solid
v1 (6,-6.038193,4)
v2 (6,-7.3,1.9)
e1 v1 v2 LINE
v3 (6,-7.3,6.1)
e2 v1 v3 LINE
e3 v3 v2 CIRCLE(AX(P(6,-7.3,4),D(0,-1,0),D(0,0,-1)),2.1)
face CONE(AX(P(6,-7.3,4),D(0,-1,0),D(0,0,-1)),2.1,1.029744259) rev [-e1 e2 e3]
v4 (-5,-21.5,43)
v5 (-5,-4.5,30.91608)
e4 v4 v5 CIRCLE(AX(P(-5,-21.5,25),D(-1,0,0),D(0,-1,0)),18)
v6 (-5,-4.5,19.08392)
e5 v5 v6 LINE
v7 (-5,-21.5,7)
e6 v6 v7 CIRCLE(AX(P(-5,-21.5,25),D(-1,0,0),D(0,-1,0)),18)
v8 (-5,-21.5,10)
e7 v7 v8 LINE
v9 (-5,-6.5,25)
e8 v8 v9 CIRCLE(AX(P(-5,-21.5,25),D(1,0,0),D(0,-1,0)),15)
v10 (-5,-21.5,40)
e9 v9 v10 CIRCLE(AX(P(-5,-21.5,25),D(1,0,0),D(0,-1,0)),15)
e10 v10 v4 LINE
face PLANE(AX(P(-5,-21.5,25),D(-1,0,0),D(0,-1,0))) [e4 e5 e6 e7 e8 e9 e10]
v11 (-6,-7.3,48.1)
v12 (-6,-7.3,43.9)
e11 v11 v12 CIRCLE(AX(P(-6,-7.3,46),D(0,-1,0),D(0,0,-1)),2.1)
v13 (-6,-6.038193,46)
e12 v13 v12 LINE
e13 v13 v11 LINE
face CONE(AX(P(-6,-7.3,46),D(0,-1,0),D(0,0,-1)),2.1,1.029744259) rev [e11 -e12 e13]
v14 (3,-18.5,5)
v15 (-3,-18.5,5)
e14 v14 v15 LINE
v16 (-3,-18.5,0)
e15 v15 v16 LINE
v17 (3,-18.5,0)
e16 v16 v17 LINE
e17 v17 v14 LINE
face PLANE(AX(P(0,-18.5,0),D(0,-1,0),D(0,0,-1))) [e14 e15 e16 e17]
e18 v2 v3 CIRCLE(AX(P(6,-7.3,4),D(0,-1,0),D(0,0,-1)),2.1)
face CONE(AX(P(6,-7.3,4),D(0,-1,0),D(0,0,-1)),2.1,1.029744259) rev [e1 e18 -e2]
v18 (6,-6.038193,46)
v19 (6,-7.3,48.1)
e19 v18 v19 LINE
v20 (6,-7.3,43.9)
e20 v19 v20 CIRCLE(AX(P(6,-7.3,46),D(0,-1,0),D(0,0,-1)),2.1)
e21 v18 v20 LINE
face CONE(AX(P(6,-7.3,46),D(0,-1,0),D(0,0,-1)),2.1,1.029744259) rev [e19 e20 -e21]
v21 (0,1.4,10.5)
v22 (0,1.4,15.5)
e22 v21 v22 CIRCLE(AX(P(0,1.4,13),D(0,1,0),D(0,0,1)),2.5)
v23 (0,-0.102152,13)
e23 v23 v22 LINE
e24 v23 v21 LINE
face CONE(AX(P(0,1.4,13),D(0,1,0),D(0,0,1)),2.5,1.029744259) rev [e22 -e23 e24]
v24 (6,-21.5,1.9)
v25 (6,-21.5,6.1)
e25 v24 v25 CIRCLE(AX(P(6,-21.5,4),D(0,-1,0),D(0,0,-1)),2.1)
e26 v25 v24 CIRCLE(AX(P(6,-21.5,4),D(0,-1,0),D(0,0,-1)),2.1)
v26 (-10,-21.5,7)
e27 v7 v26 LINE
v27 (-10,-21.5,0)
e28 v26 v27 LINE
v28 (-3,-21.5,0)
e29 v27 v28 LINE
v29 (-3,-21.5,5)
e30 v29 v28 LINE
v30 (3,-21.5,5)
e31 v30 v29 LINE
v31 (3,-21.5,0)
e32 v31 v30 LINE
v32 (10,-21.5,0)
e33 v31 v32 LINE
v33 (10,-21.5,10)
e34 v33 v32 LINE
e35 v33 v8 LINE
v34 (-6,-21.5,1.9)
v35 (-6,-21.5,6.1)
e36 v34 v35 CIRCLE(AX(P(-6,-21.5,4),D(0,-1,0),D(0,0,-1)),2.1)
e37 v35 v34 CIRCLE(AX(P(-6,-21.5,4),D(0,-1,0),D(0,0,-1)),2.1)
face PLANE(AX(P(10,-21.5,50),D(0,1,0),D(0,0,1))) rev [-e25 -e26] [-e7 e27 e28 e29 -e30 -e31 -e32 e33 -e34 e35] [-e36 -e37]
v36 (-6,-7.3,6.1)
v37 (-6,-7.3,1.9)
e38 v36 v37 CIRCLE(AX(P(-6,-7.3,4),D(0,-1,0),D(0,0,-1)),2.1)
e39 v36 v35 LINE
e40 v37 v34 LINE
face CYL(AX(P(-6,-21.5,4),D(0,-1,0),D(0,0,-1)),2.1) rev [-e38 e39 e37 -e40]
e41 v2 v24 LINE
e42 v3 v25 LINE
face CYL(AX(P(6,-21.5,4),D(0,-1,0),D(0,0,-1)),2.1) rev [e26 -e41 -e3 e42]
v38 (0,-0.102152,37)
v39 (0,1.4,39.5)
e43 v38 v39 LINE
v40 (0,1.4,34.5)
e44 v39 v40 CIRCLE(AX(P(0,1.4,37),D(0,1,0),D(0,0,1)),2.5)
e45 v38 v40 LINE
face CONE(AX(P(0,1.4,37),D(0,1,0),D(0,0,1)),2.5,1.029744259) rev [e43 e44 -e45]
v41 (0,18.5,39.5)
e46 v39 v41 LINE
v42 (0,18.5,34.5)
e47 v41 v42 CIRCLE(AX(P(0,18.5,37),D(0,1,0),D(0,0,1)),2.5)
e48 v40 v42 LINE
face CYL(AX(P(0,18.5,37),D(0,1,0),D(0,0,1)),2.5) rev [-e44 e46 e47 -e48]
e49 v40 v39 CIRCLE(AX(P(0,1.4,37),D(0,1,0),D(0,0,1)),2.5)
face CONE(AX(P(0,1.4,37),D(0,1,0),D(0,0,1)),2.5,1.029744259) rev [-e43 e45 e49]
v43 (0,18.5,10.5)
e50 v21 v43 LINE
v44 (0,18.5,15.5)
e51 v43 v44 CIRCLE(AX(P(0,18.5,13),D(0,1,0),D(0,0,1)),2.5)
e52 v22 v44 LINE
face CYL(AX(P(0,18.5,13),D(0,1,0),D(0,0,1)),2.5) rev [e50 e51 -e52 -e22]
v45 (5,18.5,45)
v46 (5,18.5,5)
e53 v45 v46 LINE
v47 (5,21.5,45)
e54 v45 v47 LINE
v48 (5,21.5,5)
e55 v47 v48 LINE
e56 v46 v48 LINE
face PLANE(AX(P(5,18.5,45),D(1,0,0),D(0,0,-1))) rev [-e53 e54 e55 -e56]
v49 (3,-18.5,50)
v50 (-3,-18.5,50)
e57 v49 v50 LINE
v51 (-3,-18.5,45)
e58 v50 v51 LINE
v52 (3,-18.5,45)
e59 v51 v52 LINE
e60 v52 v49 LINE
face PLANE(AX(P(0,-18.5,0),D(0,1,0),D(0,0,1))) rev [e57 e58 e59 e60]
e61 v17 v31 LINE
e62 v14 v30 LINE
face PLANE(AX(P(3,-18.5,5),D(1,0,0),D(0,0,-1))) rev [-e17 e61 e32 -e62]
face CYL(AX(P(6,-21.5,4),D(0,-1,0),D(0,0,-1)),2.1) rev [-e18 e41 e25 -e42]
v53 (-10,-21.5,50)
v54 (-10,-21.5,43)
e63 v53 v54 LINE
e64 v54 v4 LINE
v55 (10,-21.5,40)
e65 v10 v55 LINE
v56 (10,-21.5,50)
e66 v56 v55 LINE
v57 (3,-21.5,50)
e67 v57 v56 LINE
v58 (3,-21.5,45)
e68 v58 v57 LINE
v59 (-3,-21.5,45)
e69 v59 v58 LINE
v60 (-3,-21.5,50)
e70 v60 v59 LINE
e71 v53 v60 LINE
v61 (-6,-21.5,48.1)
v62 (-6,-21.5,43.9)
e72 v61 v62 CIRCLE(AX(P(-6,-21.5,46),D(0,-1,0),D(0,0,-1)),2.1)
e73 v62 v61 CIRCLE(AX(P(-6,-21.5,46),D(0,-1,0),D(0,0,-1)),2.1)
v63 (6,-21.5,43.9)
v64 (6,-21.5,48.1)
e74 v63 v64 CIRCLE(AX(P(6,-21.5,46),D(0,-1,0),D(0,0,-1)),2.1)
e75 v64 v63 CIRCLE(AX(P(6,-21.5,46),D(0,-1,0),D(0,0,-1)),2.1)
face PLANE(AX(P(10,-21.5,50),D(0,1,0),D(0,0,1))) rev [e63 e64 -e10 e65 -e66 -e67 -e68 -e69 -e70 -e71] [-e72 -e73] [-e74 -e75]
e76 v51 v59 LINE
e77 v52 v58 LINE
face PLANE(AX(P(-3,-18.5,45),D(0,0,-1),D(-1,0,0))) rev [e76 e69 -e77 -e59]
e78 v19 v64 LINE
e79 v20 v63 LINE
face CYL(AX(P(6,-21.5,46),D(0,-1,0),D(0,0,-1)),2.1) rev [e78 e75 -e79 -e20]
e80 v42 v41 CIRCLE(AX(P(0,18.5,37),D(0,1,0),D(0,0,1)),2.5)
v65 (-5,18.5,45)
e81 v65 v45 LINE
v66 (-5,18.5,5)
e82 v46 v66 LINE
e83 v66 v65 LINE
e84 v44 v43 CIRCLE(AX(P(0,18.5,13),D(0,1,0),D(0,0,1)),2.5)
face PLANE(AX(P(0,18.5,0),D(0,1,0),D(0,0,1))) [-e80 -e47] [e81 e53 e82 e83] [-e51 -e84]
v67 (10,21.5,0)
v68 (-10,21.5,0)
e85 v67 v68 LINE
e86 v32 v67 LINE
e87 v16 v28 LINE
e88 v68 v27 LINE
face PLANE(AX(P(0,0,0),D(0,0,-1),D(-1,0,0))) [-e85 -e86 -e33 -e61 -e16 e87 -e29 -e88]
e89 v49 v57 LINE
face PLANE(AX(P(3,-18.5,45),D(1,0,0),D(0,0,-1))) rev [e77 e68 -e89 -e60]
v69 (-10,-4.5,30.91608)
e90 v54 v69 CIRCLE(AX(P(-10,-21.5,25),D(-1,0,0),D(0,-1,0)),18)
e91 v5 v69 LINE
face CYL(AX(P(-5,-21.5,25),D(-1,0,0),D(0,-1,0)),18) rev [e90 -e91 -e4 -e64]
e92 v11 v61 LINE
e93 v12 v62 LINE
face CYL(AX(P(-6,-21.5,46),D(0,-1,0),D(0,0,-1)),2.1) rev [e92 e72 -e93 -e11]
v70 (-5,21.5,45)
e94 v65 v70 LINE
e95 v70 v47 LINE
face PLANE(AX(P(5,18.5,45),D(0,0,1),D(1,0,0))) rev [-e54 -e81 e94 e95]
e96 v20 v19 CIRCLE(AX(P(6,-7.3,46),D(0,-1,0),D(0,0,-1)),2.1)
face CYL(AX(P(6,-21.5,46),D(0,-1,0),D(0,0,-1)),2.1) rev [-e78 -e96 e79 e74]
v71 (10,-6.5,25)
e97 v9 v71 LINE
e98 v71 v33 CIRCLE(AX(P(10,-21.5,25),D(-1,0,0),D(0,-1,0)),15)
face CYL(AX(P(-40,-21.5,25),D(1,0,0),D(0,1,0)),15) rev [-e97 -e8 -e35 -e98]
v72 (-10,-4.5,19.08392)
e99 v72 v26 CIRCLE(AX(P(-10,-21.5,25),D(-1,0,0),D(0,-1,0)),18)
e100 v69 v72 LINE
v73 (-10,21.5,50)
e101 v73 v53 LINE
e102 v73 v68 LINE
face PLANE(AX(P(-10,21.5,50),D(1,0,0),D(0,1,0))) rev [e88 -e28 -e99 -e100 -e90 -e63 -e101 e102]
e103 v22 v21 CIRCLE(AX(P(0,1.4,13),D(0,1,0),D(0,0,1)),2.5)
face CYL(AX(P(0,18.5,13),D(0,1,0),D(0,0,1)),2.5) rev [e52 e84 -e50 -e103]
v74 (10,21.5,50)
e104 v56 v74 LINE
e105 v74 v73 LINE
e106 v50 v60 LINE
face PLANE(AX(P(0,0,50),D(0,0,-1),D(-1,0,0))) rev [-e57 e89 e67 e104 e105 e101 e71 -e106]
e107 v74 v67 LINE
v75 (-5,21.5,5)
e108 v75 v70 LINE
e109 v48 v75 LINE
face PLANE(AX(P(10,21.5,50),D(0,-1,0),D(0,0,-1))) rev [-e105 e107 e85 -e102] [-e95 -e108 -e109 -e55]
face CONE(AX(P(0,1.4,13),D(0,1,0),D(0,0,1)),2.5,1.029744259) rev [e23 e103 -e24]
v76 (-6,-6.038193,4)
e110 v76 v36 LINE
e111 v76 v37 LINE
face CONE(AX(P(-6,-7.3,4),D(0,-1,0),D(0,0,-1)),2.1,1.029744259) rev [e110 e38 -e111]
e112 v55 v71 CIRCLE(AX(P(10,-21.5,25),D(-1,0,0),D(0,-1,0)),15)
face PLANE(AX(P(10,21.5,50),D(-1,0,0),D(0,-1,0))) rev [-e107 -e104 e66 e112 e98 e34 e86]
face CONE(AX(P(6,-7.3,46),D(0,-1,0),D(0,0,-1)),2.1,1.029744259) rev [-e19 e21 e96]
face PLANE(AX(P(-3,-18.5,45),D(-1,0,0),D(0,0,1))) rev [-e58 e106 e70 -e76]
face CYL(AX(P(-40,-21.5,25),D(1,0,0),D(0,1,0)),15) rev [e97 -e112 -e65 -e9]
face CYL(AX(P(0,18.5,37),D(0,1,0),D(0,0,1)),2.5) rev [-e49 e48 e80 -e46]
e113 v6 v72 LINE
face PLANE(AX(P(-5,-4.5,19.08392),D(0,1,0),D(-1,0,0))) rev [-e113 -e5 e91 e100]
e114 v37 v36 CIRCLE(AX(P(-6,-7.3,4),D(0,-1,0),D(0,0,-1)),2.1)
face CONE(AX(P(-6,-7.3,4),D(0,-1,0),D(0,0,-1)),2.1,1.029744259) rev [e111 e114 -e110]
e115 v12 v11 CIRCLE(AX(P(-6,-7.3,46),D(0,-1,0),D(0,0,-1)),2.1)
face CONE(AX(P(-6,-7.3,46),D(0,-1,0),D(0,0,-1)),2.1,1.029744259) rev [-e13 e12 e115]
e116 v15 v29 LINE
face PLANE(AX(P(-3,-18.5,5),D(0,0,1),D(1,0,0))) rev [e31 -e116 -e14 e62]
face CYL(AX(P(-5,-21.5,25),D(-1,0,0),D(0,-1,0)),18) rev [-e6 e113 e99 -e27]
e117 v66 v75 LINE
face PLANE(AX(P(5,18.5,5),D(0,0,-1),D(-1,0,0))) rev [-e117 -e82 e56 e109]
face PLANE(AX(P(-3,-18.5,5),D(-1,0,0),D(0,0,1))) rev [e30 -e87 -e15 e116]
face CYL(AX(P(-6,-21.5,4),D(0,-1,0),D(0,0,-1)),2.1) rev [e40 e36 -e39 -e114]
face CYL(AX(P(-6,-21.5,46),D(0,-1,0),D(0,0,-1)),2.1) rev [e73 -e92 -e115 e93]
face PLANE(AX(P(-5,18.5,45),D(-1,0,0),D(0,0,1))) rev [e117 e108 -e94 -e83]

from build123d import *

# Parameters (mm, degrees)
SKETCH1_W                  = 20
SKETCH1_H                  = 43
BOSS_EXTRUDE1_DEPTH        = 50
SKETCH2_R                  = 15
CUT_EXTRUDE1_DEPTH         = 50
CUT_EXTRUDE2_DEPTH         = 5
SKETCH4_W                  = 6
SKETCH4_H                  = 5
CUT_EXTRUDE3_DEPTH         = 3
SIZE_MM_DOWEL_HOLE_1_D     = 4.2
SIZE_MM_DOWEL_HOLE_1_DEPTH = 14.2
SIZE_MM_DOWEL_HOLE_1_TIP   = 1.2618073
SKETCH8_W                  = 10
SKETCH8_H                  = 40
CUT_EXTRUDE4_DEPTH         = 3
SIZE_MM_DOWEL_HOLE_2_D     = 5
SIZE_MM_DOWEL_HOLE_2_DEPTH = 17.1
SIZE_MM_DOWEL_HOLE_2_TIP   = 1.502151548


with BuildPart() as part:
    # Sketch1 → Boss-Extrude1 (new body)
    with BuildSketch(Plane.XY):
        Rectangle(SKETCH1_W, SKETCH1_H)
    extrude(amount=BOSS_EXTRUDE1_DEPTH)

    # Sketch2 → Cut-Extrude1 (cut)
    with BuildSketch(Plane(origin=(10, 0, 0), x_dir=(0, 0, -1), z_dir=(1, 0, 0))):
        with Locations((-25, -21.5)):
            Circle(SKETCH2_R)
    extrude(amount=-CUT_EXTRUDE1_DEPTH, mode=Mode.SUBTRACT)

    # Sketch3 → Cut-Extrude2 (cut)
    with BuildSketch(Plane.ZY.offset(10)):
        with BuildLine():
            Line((19.083920217, -4.5), (30.916079783, -4.5))
            ThreePointArc((30.916079783, -4.5), (25, -39.5), (19.083920217, -4.5))
        make_face()
    extrude(amount=-CUT_EXTRUDE2_DEPTH, mode=Mode.SUBTRACT)

    # Sketch4 → Cut-Extrude3 (cut)
    with BuildSketch(Plane.XZ.offset(21.5)):
        with Locations((0, 2.5)):
            Rectangle(SKETCH4_W, SKETCH4_H)
        with Locations((0, 47.5)):
            Rectangle(SKETCH4_W, SKETCH4_H)
    extrude(amount=-CUT_EXTRUDE3_DEPTH, mode=Mode.SUBTRACT)

    # Size mm Dowel hole 1
    with Locations(Plane(origin=(0, -21.5, 0), x_dir=(-1, 0, 0), z_dir=(0, -1, 0))):
        with Locations((6, -4), (-6, -4), (6, -46), (-6, -46)):
            Hole(SIZE_MM_DOWEL_HOLE_1_D / 2, depth=SIZE_MM_DOWEL_HOLE_1_DEPTH)
            with Locations((0, 0, -(SIZE_MM_DOWEL_HOLE_1_DEPTH + SIZE_MM_DOWEL_HOLE_1_TIP / 2))):  # 118° drill point
                Cone(0, SIZE_MM_DOWEL_HOLE_1_D / 2, SIZE_MM_DOWEL_HOLE_1_TIP, mode=Mode.SUBTRACT)

    # Sketch8 → Cut-Extrude4 (cut)
    with BuildSketch(Plane(origin=(0, 21.5, 0), x_dir=(1, 0, 0), z_dir=(0, 1, 0))):
        with Locations((0, -25)):
            Rectangle(SKETCH8_W, SKETCH8_H)
    extrude(amount=-CUT_EXTRUDE4_DEPTH, mode=Mode.SUBTRACT)

    # Size mm Dowel hole 2
    with Locations(Plane(origin=(0, 18.5, 0), x_dir=(1, 0, 0), z_dir=(0, 1, 0))):
        with Locations((0, -13), (0, -37)):
            Hole(SIZE_MM_DOWEL_HOLE_2_D / 2, depth=SIZE_MM_DOWEL_HOLE_2_DEPTH)
            with Locations((0, 0, -(SIZE_MM_DOWEL_HOLE_2_DEPTH + SIZE_MM_DOWEL_HOLE_2_TIP / 2))):  # 118° drill point
                Cone(0, SIZE_MM_DOWEL_HOLE_2_D / 2, SIZE_MM_DOWEL_HOLE_2_TIP, mode=Mode.SUBTRACT)


solid = part.part
